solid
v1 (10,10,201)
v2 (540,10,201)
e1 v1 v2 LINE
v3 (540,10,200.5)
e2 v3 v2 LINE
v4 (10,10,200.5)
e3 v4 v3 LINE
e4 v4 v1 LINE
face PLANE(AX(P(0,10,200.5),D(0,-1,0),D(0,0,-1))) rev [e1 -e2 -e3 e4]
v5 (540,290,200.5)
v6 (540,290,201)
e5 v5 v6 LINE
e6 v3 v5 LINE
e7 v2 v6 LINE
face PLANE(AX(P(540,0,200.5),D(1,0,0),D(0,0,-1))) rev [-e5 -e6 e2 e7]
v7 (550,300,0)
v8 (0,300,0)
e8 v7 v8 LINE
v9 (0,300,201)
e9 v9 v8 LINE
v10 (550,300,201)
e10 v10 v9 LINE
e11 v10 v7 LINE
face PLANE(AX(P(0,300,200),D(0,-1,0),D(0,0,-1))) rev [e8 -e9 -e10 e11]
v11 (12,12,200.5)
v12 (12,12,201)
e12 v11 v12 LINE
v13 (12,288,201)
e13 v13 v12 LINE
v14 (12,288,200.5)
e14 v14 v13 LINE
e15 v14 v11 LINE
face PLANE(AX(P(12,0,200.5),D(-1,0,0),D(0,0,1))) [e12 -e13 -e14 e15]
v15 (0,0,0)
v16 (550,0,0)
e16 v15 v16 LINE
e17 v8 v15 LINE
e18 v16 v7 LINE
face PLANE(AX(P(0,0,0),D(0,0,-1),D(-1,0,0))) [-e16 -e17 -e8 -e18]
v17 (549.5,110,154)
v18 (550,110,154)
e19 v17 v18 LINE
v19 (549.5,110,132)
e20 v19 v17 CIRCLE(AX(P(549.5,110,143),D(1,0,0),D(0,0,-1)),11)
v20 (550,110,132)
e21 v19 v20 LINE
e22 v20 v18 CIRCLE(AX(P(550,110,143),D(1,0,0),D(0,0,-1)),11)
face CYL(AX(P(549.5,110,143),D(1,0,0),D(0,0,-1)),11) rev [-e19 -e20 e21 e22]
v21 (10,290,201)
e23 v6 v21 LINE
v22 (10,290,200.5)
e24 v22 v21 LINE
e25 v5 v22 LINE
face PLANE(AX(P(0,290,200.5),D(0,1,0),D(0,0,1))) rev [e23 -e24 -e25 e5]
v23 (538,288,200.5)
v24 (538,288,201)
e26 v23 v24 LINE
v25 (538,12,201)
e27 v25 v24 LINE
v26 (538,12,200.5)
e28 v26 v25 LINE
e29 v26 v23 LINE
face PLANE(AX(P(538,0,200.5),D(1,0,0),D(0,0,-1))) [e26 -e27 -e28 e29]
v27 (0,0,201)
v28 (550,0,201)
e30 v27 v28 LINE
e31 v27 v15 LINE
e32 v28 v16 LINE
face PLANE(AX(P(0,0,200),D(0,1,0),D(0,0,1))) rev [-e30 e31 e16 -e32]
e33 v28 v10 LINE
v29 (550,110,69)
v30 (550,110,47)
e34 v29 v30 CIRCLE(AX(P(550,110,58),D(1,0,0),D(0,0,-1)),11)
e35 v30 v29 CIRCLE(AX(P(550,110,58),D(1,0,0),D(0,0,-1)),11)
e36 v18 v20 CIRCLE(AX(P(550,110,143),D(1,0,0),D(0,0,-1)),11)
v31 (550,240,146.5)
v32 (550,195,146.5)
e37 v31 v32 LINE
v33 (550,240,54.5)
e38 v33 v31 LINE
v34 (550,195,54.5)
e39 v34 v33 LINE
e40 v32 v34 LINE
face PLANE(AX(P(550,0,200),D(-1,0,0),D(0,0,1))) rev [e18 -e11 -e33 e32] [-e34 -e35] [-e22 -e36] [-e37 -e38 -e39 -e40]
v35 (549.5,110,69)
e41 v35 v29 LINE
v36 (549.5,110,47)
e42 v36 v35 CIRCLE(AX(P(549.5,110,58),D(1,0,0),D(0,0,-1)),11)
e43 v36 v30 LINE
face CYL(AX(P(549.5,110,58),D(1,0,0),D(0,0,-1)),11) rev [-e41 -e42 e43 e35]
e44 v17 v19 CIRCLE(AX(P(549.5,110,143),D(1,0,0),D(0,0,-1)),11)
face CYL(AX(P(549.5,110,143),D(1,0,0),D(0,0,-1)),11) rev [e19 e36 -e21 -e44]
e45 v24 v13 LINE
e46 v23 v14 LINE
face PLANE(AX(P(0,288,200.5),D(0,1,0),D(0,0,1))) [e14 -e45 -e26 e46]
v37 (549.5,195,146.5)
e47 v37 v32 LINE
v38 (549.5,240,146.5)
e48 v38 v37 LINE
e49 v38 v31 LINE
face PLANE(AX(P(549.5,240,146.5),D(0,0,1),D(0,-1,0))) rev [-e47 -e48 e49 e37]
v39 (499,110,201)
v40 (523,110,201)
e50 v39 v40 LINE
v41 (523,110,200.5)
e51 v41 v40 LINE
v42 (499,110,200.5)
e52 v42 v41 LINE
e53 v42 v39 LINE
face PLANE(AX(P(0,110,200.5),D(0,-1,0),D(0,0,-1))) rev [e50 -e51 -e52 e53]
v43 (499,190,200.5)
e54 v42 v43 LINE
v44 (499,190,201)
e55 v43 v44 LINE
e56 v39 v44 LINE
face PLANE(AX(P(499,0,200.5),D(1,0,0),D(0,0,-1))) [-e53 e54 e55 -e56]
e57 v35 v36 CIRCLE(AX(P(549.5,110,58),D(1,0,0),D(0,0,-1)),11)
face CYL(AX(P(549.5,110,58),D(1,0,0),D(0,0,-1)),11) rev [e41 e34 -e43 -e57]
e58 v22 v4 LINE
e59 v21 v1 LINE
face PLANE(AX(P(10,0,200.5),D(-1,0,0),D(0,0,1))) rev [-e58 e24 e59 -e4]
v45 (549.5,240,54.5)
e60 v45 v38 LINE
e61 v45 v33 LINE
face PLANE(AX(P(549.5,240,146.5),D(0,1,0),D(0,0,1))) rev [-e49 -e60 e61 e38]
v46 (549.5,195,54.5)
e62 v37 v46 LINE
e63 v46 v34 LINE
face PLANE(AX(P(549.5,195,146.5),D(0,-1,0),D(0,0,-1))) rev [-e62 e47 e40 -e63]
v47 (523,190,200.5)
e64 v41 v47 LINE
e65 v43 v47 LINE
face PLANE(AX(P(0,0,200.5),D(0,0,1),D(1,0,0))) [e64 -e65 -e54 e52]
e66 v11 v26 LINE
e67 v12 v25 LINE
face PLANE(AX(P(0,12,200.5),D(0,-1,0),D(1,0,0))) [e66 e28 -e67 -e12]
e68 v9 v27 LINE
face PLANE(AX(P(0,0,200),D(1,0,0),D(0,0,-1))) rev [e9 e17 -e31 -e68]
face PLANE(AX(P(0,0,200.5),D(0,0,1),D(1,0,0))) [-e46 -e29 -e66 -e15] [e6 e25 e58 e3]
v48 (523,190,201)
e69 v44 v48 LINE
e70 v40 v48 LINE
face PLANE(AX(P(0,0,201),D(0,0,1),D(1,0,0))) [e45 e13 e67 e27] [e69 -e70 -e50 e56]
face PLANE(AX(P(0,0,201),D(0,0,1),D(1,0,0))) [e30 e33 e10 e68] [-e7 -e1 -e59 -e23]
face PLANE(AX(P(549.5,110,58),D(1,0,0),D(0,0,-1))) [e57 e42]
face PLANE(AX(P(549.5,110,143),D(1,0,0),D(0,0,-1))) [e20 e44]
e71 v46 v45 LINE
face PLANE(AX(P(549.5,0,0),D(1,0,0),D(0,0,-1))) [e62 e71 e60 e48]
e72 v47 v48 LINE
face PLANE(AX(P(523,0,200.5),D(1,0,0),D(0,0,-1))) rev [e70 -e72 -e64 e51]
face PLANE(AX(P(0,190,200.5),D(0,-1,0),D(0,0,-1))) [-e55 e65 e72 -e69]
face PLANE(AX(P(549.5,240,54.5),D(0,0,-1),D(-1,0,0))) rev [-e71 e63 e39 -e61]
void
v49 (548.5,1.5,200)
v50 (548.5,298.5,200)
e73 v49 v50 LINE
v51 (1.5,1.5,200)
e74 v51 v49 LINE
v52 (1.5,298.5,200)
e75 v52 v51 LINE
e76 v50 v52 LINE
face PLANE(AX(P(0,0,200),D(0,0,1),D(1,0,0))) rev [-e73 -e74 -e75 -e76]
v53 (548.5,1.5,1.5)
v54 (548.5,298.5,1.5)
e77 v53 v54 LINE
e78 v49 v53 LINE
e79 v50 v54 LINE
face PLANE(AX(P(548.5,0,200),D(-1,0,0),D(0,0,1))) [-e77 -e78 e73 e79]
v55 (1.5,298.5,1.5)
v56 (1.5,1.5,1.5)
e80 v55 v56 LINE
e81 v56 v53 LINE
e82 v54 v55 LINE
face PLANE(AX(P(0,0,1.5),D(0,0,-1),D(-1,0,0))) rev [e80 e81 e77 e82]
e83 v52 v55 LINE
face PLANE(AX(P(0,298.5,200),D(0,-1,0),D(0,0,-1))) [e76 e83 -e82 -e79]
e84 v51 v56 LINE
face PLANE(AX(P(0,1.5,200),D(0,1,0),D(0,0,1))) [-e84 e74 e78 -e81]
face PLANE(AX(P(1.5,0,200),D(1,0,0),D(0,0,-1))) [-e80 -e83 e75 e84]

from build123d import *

# Parameters (mm, degrees)
SKETCH1_W           = 550
SKETCH1_H           = 300
BOSS_EXTRUDE1_DEPTH = 200
SHELL1_T            = -1.5
SKETCH2_W           = 550
SKETCH2_H           = 300
BOSS_EXTRUDE2_DEPTH = 1
SKETCH3_W           = 530
SKETCH3_H           = 280
SKETCH3_W_2         = 526
SKETCH3_H_2         = 276
SKETCH3_W_3         = 24
SKETCH3_H_3         = 80
CUT_EXTRUDE1_DEPTH  = 0.5
SKETCH5_R           = 11
SKETCH5_W           = 92
SKETCH5_H           = 45
CUT_EXTRUDE2_DEPTH  = 0.5


with BuildPart() as part:
    # Sketch1 → Boss-Extrude1 (new body)
    with BuildSketch(Plane.XY):
        with Locations((275, 150)):
            Rectangle(SKETCH1_W, SKETCH1_H)
    extrude(amount=BOSS_EXTRUDE1_DEPTH)

    # Shell1
    shell1_openings = [part.faces().sort_by_distance(p)[0] for p in [
        (275, 150, 200),
    ]]
    offset(amount=SHELL1_T, openings=shell1_openings, kind=Kind.INTERSECTION)

    # Sketch2 → Boss-Extrude2 (add)
    with BuildSketch(Plane.XY.offset(200)):
        with Locations((275, 150)):
            Rectangle(SKETCH2_W, SKETCH2_H)
    extrude(amount=BOSS_EXTRUDE2_DEPTH)

    # Sketch3 → Cut-Extrude1 (cut)
    # profile 1 of 2: a face of its own
    with BuildSketch(Plane.XY.offset(201)):
        with Locations((275, 150)):
            Rectangle(SKETCH3_W, SKETCH3_H)
        with Locations((275, 150)):
            Rectangle(SKETCH3_W_2, SKETCH3_H_2, mode=Mode.SUBTRACT)
    # profile 2 of 2: a face of its own
    with BuildSketch(Plane.XY.offset(201)):
        with Locations((511, 150)):
            Rectangle(SKETCH3_W_3, SKETCH3_H_3)
    extrude(amount=-CUT_EXTRUDE1_DEPTH, mode=Mode.SUBTRACT)

    # Sketch5 → Cut-Extrude2 (cut)
    with BuildSketch(Plane(origin=(550, 0, 0), x_dir=(0, 0, -1), z_dir=(1, 0, 0))):
        with Locations((-143, 110)):
            Circle(SKETCH5_R)
        with Locations((-58, 110)):
            Circle(SKETCH5_R)
        with Locations((-100.5, 217.5)):
            Rectangle(SKETCH5_W, SKETCH5_H)
    extrude(amount=-CUT_EXTRUDE2_DEPTH, mode=Mode.SUBTRACT)


solid = part.part
